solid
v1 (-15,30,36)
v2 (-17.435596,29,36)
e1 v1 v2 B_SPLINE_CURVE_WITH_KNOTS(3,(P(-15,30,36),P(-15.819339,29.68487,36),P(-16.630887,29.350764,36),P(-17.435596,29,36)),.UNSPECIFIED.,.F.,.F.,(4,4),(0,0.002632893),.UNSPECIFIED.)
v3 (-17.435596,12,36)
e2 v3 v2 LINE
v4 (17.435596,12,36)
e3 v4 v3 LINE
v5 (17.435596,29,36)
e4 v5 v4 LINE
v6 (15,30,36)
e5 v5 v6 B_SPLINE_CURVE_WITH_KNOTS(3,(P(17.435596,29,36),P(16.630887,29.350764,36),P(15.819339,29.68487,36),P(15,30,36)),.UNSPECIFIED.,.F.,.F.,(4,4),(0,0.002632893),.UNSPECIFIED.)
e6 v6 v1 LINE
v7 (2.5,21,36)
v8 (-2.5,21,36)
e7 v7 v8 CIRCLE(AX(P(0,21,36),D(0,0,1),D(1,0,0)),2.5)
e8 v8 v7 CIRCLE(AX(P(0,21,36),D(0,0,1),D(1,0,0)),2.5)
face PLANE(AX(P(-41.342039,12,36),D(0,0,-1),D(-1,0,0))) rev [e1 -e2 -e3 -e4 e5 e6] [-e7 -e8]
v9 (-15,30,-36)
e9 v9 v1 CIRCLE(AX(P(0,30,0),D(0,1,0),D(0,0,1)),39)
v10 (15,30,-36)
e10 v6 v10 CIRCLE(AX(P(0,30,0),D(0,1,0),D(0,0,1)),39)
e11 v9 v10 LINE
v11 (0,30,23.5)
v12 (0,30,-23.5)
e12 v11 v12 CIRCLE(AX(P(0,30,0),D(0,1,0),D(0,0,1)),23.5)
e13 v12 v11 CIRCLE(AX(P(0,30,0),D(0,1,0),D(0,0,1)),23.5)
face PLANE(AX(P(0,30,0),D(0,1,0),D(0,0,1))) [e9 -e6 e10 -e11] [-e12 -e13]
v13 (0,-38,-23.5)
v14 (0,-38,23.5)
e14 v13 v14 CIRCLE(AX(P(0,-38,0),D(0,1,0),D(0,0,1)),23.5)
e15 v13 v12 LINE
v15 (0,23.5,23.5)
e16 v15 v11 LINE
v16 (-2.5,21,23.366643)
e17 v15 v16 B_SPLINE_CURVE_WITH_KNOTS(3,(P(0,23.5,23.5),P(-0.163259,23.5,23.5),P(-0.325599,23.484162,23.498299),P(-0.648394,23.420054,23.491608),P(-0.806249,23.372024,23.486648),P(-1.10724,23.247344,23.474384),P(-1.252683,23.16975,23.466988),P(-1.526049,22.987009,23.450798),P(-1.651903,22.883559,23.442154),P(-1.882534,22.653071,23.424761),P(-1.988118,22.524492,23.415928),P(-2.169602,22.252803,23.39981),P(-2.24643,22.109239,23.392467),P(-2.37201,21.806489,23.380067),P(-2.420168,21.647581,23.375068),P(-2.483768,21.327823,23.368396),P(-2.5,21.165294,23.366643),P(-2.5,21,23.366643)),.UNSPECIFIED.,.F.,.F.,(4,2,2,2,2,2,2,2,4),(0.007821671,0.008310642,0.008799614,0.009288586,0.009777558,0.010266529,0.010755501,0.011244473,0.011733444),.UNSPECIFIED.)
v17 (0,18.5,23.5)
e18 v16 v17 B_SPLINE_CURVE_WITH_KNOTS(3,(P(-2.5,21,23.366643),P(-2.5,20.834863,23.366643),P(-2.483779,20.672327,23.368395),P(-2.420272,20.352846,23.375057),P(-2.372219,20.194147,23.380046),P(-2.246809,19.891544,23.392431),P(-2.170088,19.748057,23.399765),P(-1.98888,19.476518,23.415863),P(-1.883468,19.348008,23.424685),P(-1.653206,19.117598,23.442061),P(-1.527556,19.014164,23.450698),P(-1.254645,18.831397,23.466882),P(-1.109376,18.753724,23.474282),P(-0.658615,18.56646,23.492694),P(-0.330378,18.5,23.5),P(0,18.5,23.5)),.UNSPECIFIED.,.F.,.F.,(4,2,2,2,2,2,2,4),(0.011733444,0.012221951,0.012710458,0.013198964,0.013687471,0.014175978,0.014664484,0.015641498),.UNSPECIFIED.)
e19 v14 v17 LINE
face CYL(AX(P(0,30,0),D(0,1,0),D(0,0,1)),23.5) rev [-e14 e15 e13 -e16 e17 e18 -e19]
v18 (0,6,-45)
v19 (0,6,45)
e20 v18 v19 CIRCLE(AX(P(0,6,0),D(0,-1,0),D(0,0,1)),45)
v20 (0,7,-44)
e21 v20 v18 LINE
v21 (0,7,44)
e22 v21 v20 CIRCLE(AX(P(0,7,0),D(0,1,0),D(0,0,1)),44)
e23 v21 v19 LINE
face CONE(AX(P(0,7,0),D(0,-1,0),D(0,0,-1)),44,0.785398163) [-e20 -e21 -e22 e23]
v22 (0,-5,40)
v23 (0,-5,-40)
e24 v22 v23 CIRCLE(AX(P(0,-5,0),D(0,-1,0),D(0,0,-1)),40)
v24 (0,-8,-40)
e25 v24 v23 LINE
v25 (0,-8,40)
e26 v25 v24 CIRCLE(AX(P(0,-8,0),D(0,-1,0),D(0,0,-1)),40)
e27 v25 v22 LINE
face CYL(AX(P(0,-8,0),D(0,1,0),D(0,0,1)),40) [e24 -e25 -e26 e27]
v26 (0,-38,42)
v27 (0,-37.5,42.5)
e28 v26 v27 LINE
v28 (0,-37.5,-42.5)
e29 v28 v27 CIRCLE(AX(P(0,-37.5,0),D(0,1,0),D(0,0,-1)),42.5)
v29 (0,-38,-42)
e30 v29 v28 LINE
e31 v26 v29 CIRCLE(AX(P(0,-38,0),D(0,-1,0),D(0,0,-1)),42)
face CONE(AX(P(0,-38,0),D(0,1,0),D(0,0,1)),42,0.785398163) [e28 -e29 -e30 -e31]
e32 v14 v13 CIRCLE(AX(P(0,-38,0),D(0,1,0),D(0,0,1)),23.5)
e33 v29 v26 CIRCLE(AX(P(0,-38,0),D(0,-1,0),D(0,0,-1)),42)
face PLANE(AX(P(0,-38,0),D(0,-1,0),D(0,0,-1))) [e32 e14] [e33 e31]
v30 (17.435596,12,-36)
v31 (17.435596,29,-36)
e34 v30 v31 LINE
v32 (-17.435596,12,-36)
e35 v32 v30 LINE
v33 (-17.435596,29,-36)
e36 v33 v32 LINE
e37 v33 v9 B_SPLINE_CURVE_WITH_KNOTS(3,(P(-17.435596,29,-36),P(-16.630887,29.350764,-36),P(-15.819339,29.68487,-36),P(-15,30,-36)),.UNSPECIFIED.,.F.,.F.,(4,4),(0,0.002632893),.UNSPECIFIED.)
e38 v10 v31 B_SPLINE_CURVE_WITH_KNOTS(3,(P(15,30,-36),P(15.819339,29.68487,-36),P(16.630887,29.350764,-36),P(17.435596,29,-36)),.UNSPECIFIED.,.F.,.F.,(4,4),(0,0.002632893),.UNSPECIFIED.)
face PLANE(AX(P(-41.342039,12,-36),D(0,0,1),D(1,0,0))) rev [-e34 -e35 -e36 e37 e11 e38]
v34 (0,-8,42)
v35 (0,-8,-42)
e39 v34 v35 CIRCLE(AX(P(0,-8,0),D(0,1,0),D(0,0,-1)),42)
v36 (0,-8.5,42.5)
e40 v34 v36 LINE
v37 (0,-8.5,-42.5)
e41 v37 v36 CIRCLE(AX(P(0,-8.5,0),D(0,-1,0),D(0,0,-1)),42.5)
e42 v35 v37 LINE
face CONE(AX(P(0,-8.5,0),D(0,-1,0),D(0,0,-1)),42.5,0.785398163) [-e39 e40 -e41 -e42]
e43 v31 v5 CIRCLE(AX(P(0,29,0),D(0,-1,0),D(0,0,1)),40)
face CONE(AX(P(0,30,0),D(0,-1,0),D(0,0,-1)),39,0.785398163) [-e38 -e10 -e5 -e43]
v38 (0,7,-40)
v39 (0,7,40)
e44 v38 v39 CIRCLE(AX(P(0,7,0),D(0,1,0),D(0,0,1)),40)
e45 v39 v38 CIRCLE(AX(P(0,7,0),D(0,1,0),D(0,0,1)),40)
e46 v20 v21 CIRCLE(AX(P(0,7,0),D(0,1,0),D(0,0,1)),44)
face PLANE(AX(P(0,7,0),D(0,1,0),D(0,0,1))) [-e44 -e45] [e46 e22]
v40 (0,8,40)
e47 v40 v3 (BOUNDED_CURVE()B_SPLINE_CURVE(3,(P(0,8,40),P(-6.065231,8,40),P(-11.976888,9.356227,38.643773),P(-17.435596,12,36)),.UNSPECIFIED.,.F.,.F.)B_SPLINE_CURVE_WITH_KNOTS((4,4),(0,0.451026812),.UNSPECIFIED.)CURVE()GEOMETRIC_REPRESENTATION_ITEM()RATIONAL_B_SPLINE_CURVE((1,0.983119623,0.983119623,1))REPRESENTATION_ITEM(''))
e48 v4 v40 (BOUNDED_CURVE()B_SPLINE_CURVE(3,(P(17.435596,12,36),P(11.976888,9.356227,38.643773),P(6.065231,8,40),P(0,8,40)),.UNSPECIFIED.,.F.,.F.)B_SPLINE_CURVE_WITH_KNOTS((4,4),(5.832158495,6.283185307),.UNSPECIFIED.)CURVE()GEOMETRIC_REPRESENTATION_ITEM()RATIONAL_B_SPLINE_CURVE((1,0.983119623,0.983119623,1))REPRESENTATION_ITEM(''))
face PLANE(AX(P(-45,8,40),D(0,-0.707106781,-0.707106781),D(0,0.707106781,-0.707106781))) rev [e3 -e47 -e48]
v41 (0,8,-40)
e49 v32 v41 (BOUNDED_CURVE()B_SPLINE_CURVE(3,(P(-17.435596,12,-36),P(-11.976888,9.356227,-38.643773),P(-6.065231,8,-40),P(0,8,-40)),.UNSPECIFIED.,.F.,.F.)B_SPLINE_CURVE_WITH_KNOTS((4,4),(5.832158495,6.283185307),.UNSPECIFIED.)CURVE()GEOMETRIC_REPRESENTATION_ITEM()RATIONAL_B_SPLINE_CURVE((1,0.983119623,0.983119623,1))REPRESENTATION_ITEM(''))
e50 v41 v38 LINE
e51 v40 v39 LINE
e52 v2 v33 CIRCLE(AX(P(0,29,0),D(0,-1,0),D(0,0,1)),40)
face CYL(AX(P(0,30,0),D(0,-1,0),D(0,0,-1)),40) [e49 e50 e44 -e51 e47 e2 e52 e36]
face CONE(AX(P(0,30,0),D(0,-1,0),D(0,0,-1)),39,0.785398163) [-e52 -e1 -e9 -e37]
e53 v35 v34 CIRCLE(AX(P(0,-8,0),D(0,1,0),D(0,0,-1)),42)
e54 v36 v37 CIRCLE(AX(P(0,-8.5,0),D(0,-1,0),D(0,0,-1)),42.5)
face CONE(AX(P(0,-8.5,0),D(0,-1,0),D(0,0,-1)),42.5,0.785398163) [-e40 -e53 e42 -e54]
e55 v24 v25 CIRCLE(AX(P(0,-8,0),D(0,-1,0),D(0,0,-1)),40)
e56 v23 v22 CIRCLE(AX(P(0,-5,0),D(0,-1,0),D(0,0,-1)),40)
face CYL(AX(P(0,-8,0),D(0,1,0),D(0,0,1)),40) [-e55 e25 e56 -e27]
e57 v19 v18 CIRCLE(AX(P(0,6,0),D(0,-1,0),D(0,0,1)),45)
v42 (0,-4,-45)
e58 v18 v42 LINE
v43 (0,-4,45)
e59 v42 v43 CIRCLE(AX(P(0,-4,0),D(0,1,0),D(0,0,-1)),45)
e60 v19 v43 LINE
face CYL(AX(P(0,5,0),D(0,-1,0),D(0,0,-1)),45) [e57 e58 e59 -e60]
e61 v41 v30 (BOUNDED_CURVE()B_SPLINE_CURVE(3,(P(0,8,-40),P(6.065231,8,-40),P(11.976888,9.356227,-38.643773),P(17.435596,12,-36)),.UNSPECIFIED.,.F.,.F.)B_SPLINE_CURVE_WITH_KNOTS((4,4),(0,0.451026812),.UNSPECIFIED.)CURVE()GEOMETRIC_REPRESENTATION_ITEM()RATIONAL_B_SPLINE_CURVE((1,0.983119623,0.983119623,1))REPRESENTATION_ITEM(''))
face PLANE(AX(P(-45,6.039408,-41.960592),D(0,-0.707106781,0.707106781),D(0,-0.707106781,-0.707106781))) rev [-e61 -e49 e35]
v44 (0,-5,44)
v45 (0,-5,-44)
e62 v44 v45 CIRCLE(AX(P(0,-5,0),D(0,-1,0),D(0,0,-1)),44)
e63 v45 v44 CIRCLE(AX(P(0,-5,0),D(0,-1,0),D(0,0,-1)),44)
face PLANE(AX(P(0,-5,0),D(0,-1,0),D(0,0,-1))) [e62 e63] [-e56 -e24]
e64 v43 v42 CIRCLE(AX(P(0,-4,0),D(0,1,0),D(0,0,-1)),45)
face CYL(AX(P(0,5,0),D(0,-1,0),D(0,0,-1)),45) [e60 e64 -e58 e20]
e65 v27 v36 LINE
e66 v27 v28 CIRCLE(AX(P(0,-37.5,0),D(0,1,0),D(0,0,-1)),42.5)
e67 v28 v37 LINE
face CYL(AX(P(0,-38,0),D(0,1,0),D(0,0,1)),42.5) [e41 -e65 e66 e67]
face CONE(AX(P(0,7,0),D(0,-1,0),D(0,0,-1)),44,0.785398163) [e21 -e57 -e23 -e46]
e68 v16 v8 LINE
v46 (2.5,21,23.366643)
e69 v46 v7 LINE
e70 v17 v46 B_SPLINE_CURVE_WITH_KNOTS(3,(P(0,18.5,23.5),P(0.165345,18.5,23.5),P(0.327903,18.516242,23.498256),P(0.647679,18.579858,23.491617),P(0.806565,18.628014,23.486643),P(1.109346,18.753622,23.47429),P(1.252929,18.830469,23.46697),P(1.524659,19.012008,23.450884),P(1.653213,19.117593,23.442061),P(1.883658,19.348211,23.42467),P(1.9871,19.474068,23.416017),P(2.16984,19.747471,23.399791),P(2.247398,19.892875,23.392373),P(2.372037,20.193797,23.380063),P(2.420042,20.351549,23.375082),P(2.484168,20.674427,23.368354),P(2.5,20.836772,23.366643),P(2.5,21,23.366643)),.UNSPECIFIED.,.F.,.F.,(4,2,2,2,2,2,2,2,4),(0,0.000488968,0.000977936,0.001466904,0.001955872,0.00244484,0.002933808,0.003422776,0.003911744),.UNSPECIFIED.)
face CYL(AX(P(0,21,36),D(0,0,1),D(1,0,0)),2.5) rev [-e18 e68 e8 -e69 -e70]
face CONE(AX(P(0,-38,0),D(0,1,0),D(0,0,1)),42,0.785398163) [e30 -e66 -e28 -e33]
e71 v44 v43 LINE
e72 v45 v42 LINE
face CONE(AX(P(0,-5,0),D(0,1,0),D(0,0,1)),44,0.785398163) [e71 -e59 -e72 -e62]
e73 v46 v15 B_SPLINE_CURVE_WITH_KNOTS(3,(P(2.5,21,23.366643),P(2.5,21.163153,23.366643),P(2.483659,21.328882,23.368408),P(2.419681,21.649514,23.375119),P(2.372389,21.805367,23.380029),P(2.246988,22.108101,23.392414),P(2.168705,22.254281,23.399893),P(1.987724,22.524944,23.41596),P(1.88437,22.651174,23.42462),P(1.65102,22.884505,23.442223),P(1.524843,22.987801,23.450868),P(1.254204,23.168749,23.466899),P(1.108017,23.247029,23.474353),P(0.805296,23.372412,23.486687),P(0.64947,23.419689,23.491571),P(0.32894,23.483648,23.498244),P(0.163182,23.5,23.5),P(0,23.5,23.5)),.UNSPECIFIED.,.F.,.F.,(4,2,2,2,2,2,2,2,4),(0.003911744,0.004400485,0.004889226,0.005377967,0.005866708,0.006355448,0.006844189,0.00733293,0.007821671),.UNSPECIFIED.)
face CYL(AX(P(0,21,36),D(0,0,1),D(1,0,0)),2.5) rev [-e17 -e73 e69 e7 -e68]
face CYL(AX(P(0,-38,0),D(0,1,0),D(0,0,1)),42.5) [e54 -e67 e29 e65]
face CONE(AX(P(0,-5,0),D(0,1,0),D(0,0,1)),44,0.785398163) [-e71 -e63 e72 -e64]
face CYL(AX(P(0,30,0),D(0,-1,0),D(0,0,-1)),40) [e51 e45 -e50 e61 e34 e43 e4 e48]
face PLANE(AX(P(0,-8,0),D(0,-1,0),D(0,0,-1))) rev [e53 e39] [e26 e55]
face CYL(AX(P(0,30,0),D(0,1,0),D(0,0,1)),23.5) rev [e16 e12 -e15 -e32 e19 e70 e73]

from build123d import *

# Parameters (mm, degrees)
SKETCH1_R               = 40
BOSS_EXTRUDE1_DEPTH     = 30
SKETCH2_R               = 18
BOSS_EXTRUDE2_DEPTH     = 60
SKETCH3_W               = 77.976815456
SKETCH3_H               = 25.992271819
SKETCH3_W_2             = 92.098600933
SKETCH3_H_2             = 25.173617588
CUT_EXTRUDE1_DEPTH      = 18
SKETCH7_R               = 42.5
BOSS_EXTRUDE3_DEPTH     = 38
SKETCH14_R              = 3
CUT_EXTRUDE3_DEPTH      = 63
CUT_EXTRUDE4_START      = -30
SKETCH15_R              = 67.080871601
SKETCH15_R_2            = 40
CUT_EXTRUDE4_DEPTH      = 3
SKETCH17_R              = 45
SKETCH17_R_2            = 16.642095107
BOSS_EXTRUDE4_DEPTH     = 10
CHAMFER1_SIZE           = 1
CUT_EXTRUDE5_DEPTH      = 111.227038425
CUT_EXTRUDE5_DEPTH_BACK = 111.227038425
SKETCH20_R              = 45
BOSS_EXTRUDE5_DEPTH     = 2
CHAMFER2_SIZE           = 1
CHAMFER3_SIZE           = 1
SKETCH21_R              = 3
CUT_EXTRUDE7_DEPTH      = 2
SKETCH22_R              = 18
CUT_EXTRUDE8_DEPTH      = 94.134311615
M52X5_0_TAPPED_HOLE1_D  = 47
BOSS_EXTRUDE6_START     = -33
SKETCH25_R              = 42.5
SKETCH25_R_2            = 34.471384151
BOSS_EXTRUDE6_DEPTH     = 33
SKETCH26_OUTSIDE_W      = 120.862
SKETCH26_OUTSIDE_H      = 120.862
SKETCH26_OUTSIDE_R      = 40
CUT_EXTRUDE9_DEPTH      = 3
CHAMFER4_SIZE           = 0.5
M6_TAPPED_HOLE1_D       = 5
M6_TAPPED_HOLE1_DEPTH   = 17
M6_TAPPED_HOLE1_TIP     = 1.502151548


with BuildPart() as part:
    # Sketch1 → Boss-Extrude1 (new body)
    with BuildSketch(Plane(origin=(0, 0, 0), x_dir=(1, 0, 0), z_dir=(0, 1, 0))):
        with Locations(Location((0, 0, 0), (0, 0, 270))):
            Circle(SKETCH1_R)
    extrude(amount=BOSS_EXTRUDE1_DEPTH)

    # Sketch2 → Boss-Extrude2 (add)
    with BuildSketch(Plane(origin=(0, 30, 0), x_dir=(1, 0, 0), z_dir=(0, 1, 0))):
        with Locations(Location((0, 0, 0), (0, 0, 270))):
            Circle(SKETCH2_R)
    extrude(amount=BOSS_EXTRUDE2_DEPTH)

    # Sketch3 → Cut-Extrude1 (cut)
    with BuildSketch(Plane(origin=(0, 30, 0), x_dir=(1, 0, 0), z_dir=(0, 1, 0))):
        with Locations((-2.353630913, 48.996135909)):
            Rectangle(SKETCH3_W, SKETCH3_H)
        with Locations((4.707261826, -48.586808794)):
            Rectangle(SKETCH3_W_2, SKETCH3_H_2)
    extrude(amount=-CUT_EXTRUDE1_DEPTH, mode=Mode.SUBTRACT)

    # Sketch7 → Boss-Extrude3 (add)
    with BuildSketch(Plane.XZ):
        with Locations(Location((0, 0, 0), (0, 0, 270))):
            Circle(SKETCH7_R)
    extrude(amount=BOSS_EXTRUDE3_DEPTH)

    # Sketch14 → Cut-Extrude3 (cut)
    with BuildSketch(Plane.XZ.offset(38)):
        with Locations(Location((0, 0, 0), (0, 0, 270))):
            Circle(SKETCH14_R)
    extrude(amount=-CUT_EXTRUDE3_DEPTH, mode=Mode.SUBTRACT)

    # Sketch15 → Cut-Extrude4 (cut)
    with BuildSketch(Plane.XZ.offset(38).offset(CUT_EXTRUDE4_START)):
        Circle(SKETCH15_R)
        with Locations(Location((0, 0, 0), (0, 0, 270))):
            Circle(SKETCH15_R_2, mode=Mode.SUBTRACT)
    extrude(amount=-CUT_EXTRUDE4_DEPTH, mode=Mode.SUBTRACT)

    # Sketch17 → Boss-Extrude4 (add)
    with BuildSketch(Plane.XZ.offset(5)):
        with Locations(Location((0, 0, 0), (0, 0, 270))):
            Circle(SKETCH17_R)
        Circle(SKETCH17_R_2, mode=Mode.SUBTRACT)
    extrude(amount=-BOSS_EXTRUDE4_DEPTH)

    # Chamfer1
    chamfer1_edges = [part.edges().sort_by_distance(p)[0] for p in [
        (40, 30, 0),
        (0, -38, 42.5),
        (0, -5, 45),
        (0, 90, -18),
        (-40, 30, 0),
    ]]
    chamfer(chamfer1_edges, length=CHAMFER1_SIZE)

    # Sketch18 → Cut-Extrude5 (cut, two sides: drawn at the far end of the back side and taken through both)
    with BuildSketch(Plane(origin=(0, 0, 0), x_dir=(0, 0, -1), z_dir=(1, 0, 0)).offset(-CUT_EXTRUDE5_DEPTH_BACK)):
        Polygon((-40, 12), (-40, 8), (-36, 12), align=None)
        Polygon((36, 12), (41.96059215, 12), (41.96059215, 6.03940785), align=None)
    extrude(amount=CUT_EXTRUDE5_DEPTH + CUT_EXTRUDE5_DEPTH_BACK, mode=Mode.SUBTRACT)

    # Sketch20 → Boss-Extrude5 (add)
    with BuildSketch(Plane(origin=(0, 5, 0), x_dir=(1, 0, 0), z_dir=(0, 1, 0))):
        with Locations(Location((0, 0, 0), (0, 0, 90))):
            Circle(SKETCH20_R)
    extrude(amount=BOSS_EXTRUDE5_DEPTH)

    # Chamfer2
    chamfer2_edges = [part.edges().sort_by_distance(p)[0] for p in [
        (0, 7, 45),
    ]]
    chamfer(chamfer2_edges, length=CHAMFER2_SIZE)

    # Chamfer3
    chamfer3_edges = [part.edges().sort_by_distance(p)[0] for p in [
        (0, -8, 42.5),
    ]]
    chamfer(chamfer3_edges, length=CHAMFER3_SIZE)

    # Sketch21 → Cut-Extrude7 (cut)
    with BuildSketch(Plane.XZ.offset(-5)):
        with Locations(Location((0, 0, 0), (0, 0, 270))):
            Circle(SKETCH21_R)
    extrude(amount=-CUT_EXTRUDE7_DEPTH, mode=Mode.SUBTRACT)

    # Sketch22 → Cut-Extrude8 (cut, through all)
    with BuildSketch(Plane(origin=(0, 30, 0), x_dir=(1, 0, 0), z_dir=(0, 1, 0))):
        Circle(SKETCH22_R)
    extrude(amount=CUT_EXTRUDE8_DEPTH, mode=Mode.SUBTRACT)

    # M52x5.0 Tapped Hole1 (through all)
    with Locations(Plane(origin=(0, 30, 0), x_dir=(1, 0, 0), z_dir=(0, 1, 0))):
        with Locations((0, 0)):
            Hole(M52X5_0_TAPPED_HOLE1_D / 2)

    # Sketch25 → Boss-Extrude6 (add)
    with BuildSketch(Plane.XZ.offset(38).offset(BOSS_EXTRUDE6_START)):
        with Locations(Location((0, 0, 0), (0, 0, 270))):
            Circle(SKETCH25_R)
        Circle(SKETCH25_R_2, mode=Mode.SUBTRACT)
    extrude(amount=BOSS_EXTRUDE6_DEPTH)

    # Sketch26 outside → Cut-Extrude9 (cut)
    with BuildSketch(Plane.XZ.offset(5)):
        Rectangle(SKETCH26_OUTSIDE_W, SKETCH26_OUTSIDE_H)
        with Locations(Location((0, 0, 0), (0, 0, 244.158067237))):
            Circle(SKETCH26_OUTSIDE_R, mode=Mode.SUBTRACT)
    extrude(amount=CUT_EXTRUDE9_DEPTH, mode=Mode.SUBTRACT)

    # Chamfer4
    chamfer4_edges = [part.edges().sort_by_distance(p)[0] for p in [
        (0, -38, 42.5),
        (0, -8, 42.5),
    ]]
    chamfer(chamfer4_edges, length=CHAMFER4_SIZE)

    # M6 Tapped Hole1
    with Locations(Plane.XY.offset(36)):
        with Locations((0, 21)):
            Hole(M6_TAPPED_HOLE1_D / 2, depth=M6_TAPPED_HOLE1_DEPTH)
            with Locations((0, 0, -(M6_TAPPED_HOLE1_DEPTH + M6_TAPPED_HOLE1_TIP / 2))):  # 118° drill point
                Cone(0, M6_TAPPED_HOLE1_D / 2, M6_TAPPED_HOLE1_TIP, mode=Mode.SUBTRACT)


solid = part.part
